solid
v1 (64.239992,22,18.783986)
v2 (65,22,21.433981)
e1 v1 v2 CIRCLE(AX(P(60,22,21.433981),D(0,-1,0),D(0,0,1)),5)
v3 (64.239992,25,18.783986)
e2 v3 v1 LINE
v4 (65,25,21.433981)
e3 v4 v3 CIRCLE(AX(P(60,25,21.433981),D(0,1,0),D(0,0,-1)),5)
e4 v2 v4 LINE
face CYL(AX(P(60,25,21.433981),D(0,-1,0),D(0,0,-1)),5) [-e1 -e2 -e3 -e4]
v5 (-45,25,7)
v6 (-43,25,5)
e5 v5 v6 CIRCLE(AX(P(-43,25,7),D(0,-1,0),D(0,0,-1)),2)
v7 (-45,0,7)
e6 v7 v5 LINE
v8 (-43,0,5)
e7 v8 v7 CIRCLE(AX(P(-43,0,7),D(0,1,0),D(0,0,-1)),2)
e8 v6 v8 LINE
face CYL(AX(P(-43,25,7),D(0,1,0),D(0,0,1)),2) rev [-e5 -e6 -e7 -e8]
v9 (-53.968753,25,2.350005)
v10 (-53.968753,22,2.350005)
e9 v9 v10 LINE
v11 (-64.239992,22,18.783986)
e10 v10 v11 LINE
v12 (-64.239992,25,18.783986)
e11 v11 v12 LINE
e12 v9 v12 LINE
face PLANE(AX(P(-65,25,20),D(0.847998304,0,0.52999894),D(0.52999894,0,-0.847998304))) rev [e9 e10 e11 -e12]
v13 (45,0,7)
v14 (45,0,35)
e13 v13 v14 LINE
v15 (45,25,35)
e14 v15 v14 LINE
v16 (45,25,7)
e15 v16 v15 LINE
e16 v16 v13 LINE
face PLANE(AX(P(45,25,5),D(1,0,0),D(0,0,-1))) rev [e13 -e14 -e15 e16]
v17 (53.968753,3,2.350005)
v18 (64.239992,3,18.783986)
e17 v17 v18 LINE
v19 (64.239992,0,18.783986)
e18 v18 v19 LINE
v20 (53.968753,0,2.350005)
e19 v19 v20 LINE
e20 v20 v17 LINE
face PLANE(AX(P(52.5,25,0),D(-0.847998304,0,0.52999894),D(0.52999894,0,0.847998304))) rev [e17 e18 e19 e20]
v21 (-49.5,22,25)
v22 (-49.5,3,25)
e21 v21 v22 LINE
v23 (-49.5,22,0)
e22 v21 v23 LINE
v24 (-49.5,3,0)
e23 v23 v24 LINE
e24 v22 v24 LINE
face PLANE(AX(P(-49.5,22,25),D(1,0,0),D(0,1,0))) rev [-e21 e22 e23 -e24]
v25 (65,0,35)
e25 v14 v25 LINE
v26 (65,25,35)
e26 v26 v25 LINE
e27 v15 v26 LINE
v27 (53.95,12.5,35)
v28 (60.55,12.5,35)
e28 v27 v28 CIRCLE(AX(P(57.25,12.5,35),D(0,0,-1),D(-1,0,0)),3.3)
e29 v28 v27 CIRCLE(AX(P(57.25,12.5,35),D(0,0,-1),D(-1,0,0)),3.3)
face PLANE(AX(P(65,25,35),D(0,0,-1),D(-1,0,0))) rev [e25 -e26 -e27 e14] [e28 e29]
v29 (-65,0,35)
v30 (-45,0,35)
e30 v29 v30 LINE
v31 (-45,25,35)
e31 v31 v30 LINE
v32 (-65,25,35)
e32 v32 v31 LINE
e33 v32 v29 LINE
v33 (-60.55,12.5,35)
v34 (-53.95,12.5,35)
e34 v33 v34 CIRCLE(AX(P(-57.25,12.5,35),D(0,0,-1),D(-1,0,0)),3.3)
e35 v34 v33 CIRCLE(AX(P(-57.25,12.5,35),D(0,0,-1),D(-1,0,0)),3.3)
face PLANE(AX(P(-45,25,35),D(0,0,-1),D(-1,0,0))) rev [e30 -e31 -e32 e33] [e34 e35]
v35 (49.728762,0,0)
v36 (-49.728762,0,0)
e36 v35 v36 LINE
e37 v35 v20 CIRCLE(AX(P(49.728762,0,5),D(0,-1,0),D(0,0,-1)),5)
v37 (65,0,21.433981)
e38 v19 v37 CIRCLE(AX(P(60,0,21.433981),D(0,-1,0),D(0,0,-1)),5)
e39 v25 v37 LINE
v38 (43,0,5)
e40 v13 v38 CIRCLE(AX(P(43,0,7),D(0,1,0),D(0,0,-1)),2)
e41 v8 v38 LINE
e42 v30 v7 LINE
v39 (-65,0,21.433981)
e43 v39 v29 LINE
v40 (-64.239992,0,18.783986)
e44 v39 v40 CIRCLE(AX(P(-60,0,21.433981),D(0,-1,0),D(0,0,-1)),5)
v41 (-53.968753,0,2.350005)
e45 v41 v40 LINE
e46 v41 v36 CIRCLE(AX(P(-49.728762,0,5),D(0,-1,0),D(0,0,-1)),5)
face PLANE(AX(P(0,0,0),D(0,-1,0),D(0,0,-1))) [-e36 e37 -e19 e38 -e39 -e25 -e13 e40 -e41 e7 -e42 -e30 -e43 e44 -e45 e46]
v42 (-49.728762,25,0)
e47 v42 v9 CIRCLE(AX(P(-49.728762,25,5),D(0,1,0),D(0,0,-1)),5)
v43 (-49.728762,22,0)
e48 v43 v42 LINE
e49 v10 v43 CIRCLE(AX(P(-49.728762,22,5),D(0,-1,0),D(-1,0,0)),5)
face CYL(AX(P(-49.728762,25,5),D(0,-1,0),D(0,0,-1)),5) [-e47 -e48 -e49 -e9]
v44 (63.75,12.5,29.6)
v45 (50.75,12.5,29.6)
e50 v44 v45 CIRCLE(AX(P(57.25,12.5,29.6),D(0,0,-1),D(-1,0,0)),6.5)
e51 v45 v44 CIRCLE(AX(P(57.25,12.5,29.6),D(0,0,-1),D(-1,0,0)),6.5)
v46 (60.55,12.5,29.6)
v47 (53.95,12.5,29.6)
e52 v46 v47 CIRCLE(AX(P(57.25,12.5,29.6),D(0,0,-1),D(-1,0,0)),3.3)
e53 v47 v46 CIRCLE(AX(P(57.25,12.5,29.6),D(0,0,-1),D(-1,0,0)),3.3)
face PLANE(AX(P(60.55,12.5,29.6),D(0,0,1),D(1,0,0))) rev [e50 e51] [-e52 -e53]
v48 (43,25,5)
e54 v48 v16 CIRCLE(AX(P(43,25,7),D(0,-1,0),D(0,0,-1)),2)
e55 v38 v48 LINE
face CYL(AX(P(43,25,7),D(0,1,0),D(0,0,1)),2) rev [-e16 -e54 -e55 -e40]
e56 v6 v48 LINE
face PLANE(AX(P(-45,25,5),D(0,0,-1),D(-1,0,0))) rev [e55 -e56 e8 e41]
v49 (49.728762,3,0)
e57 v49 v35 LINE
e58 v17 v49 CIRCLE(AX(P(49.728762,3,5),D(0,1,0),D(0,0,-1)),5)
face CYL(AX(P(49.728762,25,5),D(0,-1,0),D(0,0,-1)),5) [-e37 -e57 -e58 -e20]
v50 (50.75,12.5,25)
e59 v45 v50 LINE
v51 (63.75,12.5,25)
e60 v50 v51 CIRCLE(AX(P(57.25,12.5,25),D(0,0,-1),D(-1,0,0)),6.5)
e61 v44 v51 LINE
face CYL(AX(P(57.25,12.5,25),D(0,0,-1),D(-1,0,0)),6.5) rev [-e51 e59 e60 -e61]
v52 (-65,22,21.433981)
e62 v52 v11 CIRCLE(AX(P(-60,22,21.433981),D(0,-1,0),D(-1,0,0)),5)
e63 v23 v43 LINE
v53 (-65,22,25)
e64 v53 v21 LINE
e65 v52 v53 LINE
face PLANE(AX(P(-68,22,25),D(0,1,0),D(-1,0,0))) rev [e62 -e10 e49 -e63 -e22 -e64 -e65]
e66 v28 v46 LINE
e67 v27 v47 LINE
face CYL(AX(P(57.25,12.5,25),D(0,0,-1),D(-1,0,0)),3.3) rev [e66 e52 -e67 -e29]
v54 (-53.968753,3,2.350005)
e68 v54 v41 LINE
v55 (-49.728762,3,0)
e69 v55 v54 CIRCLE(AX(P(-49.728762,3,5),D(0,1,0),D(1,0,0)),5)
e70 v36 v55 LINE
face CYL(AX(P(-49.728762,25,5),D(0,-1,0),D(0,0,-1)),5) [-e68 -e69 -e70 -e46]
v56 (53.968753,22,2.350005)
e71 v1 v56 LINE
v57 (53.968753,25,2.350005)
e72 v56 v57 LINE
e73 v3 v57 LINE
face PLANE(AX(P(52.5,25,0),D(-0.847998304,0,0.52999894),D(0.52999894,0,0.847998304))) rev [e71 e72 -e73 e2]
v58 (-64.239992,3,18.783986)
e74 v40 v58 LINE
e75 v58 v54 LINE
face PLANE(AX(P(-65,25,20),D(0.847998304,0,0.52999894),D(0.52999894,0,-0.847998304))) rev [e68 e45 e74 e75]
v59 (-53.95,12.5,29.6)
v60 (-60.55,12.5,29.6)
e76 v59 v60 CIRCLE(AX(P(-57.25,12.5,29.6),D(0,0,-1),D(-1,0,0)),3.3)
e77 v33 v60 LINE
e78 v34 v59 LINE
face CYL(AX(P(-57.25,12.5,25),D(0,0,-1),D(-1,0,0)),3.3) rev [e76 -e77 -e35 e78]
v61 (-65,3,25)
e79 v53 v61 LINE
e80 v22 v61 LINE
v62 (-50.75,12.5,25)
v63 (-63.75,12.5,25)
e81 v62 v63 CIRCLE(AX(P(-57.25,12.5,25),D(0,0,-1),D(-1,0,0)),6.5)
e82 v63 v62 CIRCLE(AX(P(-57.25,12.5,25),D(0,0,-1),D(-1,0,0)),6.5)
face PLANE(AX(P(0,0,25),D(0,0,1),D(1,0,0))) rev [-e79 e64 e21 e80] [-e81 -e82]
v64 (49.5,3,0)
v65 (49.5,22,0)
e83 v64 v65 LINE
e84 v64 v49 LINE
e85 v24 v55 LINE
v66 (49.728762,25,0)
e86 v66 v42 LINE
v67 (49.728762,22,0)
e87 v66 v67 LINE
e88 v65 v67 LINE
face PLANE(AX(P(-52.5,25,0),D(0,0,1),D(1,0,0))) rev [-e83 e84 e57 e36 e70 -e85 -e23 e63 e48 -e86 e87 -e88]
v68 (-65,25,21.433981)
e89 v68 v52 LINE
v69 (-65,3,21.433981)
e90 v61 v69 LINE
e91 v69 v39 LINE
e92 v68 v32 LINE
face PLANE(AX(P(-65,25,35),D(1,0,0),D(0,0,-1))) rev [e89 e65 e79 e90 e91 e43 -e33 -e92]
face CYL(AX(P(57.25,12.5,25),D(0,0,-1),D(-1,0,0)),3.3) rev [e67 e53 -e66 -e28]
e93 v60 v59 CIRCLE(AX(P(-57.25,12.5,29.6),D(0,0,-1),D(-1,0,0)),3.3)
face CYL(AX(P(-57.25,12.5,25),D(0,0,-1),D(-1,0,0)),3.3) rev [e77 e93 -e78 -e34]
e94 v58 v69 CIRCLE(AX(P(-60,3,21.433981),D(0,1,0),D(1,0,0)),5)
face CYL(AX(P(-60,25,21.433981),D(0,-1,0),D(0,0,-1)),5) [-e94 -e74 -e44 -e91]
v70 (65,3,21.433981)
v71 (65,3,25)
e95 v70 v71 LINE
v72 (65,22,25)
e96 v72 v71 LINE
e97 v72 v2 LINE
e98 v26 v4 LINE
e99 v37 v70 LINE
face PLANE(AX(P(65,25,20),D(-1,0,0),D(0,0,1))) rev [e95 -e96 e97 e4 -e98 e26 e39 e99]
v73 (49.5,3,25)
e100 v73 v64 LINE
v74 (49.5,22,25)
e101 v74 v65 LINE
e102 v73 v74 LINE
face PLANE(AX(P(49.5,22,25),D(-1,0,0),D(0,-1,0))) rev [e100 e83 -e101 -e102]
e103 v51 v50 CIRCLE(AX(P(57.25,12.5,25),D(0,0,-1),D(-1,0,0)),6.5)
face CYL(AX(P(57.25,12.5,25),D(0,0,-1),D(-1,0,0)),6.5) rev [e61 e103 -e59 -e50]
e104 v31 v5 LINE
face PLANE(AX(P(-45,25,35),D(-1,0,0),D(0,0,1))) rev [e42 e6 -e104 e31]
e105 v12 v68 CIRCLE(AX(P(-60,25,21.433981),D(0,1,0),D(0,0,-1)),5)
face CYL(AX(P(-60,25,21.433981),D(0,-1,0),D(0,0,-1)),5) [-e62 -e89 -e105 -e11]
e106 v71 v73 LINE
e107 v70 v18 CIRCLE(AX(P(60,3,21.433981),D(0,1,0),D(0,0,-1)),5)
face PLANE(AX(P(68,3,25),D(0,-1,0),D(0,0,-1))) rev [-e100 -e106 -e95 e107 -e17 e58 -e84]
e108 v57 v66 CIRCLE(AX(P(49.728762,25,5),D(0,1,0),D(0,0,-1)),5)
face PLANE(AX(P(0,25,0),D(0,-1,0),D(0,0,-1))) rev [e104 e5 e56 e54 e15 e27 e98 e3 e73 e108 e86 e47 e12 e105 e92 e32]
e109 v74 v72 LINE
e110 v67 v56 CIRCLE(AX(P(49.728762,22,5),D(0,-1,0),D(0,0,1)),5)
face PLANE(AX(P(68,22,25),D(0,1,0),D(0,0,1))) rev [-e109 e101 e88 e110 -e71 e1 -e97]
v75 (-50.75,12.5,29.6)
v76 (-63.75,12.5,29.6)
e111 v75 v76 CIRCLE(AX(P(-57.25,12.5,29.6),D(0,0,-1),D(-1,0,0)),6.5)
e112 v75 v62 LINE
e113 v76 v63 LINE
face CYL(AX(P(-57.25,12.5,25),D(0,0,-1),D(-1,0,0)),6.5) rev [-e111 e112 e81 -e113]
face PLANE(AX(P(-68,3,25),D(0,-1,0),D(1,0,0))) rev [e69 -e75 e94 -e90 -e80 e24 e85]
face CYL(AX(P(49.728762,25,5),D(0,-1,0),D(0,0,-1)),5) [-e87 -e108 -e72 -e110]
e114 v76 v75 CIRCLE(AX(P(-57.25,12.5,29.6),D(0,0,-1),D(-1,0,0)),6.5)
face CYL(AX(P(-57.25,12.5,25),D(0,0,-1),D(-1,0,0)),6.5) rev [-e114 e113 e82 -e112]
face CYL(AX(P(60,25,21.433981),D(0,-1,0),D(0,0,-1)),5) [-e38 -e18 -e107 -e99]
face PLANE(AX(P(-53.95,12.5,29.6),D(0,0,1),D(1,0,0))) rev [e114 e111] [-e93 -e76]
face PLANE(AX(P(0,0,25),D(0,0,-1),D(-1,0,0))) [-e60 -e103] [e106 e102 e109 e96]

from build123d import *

# Parameters (mm, degrees)
BOSS_EXTRUDE1_DEPTH                               = 25
SKETCH2_W                                         = 18.5
SKETCH2_H                                         = 19
CUT_EXTRUDE1_DEPTH                                = 25
COUNTERBORE_FOR_PAN_HEAD_SCREW_OF_M61_D           = 6.6
COUNTERBORE_FOR_PAN_HEAD_SCREW_OF_M61_CBORE_D     = 13
COUNTERBORE_FOR_PAN_HEAD_SCREW_OF_M61_CBORE_DEPTH = 4.6
FILETE1_R                                         = 5
FILETE2_R                                         = 2


with BuildPart() as part:
    # Sketch1 → Boss-Extrude1 (new body)
    with BuildSketch(Plane(origin=(0, 0, 0), x_dir=(1, 0, 0), z_dir=(0, 1, 0))):
        Polygon((-52.5, 0), (52.5, 0), (65, -20), (65, -35), (45, -35), (45, -5), (-45, -5), (-45, -35), (-65, -35), (-65, -20), align=None)
    extrude(amount=BOSS_EXTRUDE1_DEPTH)

    # Sketch2 → Cut-Extrude1 (cut)
    with BuildSketch(Plane(origin=(0, 0, 0), x_dir=(-1, 0, 0), z_dir=(0, 0, -1))):
        with Locations((-58.75, 12.5)):
            Rectangle(SKETCH2_W, SKETCH2_H)
        with Locations((58.75, 12.5)):
            Rectangle(SKETCH2_W, SKETCH2_H)
    extrude(amount=-CUT_EXTRUDE1_DEPTH, mode=Mode.SUBTRACT)

    # Counterbore for pan head screw of M61 (through all)
    with Locations(Plane(origin=(0, 0, 25), x_dir=(-1, 0, 0), z_dir=(0, 0, -1))):
        with Locations((-57.25, 12.5), (57.25, 12.5)):
            CounterBoreHole(COUNTERBORE_FOR_PAN_HEAD_SCREW_OF_M61_D / 2, COUNTERBORE_FOR_PAN_HEAD_SCREW_OF_M61_CBORE_D / 2, COUNTERBORE_FOR_PAN_HEAD_SCREW_OF_M61_CBORE_DEPTH)

    # Filete1
    filete1_edges = [part.edges().sort_by_distance(p)[0] for p in [
        (-52.5, 23.5, 0),
        (52.5, 23.5, 0),
        (65, 23.5, 20),
        (-65, 23.5, 20),
        (52.5, 1.5, 0),
        (65, 1.5, 20),
        (-52.5, 1.5, 0),
        (-65, 1.5, 20),
    ]]
    fillet(filete1_edges, radius=FILETE1_R)

    # Filete2
    filete2_edges = [part.edges().sort_by_distance(p)[0] for p in [
        (45, 12.5, 5),
        (-45, 12.5, 5),
    ]]
    fillet(filete2_edges, radius=FILETE2_R)


solid = part.part
